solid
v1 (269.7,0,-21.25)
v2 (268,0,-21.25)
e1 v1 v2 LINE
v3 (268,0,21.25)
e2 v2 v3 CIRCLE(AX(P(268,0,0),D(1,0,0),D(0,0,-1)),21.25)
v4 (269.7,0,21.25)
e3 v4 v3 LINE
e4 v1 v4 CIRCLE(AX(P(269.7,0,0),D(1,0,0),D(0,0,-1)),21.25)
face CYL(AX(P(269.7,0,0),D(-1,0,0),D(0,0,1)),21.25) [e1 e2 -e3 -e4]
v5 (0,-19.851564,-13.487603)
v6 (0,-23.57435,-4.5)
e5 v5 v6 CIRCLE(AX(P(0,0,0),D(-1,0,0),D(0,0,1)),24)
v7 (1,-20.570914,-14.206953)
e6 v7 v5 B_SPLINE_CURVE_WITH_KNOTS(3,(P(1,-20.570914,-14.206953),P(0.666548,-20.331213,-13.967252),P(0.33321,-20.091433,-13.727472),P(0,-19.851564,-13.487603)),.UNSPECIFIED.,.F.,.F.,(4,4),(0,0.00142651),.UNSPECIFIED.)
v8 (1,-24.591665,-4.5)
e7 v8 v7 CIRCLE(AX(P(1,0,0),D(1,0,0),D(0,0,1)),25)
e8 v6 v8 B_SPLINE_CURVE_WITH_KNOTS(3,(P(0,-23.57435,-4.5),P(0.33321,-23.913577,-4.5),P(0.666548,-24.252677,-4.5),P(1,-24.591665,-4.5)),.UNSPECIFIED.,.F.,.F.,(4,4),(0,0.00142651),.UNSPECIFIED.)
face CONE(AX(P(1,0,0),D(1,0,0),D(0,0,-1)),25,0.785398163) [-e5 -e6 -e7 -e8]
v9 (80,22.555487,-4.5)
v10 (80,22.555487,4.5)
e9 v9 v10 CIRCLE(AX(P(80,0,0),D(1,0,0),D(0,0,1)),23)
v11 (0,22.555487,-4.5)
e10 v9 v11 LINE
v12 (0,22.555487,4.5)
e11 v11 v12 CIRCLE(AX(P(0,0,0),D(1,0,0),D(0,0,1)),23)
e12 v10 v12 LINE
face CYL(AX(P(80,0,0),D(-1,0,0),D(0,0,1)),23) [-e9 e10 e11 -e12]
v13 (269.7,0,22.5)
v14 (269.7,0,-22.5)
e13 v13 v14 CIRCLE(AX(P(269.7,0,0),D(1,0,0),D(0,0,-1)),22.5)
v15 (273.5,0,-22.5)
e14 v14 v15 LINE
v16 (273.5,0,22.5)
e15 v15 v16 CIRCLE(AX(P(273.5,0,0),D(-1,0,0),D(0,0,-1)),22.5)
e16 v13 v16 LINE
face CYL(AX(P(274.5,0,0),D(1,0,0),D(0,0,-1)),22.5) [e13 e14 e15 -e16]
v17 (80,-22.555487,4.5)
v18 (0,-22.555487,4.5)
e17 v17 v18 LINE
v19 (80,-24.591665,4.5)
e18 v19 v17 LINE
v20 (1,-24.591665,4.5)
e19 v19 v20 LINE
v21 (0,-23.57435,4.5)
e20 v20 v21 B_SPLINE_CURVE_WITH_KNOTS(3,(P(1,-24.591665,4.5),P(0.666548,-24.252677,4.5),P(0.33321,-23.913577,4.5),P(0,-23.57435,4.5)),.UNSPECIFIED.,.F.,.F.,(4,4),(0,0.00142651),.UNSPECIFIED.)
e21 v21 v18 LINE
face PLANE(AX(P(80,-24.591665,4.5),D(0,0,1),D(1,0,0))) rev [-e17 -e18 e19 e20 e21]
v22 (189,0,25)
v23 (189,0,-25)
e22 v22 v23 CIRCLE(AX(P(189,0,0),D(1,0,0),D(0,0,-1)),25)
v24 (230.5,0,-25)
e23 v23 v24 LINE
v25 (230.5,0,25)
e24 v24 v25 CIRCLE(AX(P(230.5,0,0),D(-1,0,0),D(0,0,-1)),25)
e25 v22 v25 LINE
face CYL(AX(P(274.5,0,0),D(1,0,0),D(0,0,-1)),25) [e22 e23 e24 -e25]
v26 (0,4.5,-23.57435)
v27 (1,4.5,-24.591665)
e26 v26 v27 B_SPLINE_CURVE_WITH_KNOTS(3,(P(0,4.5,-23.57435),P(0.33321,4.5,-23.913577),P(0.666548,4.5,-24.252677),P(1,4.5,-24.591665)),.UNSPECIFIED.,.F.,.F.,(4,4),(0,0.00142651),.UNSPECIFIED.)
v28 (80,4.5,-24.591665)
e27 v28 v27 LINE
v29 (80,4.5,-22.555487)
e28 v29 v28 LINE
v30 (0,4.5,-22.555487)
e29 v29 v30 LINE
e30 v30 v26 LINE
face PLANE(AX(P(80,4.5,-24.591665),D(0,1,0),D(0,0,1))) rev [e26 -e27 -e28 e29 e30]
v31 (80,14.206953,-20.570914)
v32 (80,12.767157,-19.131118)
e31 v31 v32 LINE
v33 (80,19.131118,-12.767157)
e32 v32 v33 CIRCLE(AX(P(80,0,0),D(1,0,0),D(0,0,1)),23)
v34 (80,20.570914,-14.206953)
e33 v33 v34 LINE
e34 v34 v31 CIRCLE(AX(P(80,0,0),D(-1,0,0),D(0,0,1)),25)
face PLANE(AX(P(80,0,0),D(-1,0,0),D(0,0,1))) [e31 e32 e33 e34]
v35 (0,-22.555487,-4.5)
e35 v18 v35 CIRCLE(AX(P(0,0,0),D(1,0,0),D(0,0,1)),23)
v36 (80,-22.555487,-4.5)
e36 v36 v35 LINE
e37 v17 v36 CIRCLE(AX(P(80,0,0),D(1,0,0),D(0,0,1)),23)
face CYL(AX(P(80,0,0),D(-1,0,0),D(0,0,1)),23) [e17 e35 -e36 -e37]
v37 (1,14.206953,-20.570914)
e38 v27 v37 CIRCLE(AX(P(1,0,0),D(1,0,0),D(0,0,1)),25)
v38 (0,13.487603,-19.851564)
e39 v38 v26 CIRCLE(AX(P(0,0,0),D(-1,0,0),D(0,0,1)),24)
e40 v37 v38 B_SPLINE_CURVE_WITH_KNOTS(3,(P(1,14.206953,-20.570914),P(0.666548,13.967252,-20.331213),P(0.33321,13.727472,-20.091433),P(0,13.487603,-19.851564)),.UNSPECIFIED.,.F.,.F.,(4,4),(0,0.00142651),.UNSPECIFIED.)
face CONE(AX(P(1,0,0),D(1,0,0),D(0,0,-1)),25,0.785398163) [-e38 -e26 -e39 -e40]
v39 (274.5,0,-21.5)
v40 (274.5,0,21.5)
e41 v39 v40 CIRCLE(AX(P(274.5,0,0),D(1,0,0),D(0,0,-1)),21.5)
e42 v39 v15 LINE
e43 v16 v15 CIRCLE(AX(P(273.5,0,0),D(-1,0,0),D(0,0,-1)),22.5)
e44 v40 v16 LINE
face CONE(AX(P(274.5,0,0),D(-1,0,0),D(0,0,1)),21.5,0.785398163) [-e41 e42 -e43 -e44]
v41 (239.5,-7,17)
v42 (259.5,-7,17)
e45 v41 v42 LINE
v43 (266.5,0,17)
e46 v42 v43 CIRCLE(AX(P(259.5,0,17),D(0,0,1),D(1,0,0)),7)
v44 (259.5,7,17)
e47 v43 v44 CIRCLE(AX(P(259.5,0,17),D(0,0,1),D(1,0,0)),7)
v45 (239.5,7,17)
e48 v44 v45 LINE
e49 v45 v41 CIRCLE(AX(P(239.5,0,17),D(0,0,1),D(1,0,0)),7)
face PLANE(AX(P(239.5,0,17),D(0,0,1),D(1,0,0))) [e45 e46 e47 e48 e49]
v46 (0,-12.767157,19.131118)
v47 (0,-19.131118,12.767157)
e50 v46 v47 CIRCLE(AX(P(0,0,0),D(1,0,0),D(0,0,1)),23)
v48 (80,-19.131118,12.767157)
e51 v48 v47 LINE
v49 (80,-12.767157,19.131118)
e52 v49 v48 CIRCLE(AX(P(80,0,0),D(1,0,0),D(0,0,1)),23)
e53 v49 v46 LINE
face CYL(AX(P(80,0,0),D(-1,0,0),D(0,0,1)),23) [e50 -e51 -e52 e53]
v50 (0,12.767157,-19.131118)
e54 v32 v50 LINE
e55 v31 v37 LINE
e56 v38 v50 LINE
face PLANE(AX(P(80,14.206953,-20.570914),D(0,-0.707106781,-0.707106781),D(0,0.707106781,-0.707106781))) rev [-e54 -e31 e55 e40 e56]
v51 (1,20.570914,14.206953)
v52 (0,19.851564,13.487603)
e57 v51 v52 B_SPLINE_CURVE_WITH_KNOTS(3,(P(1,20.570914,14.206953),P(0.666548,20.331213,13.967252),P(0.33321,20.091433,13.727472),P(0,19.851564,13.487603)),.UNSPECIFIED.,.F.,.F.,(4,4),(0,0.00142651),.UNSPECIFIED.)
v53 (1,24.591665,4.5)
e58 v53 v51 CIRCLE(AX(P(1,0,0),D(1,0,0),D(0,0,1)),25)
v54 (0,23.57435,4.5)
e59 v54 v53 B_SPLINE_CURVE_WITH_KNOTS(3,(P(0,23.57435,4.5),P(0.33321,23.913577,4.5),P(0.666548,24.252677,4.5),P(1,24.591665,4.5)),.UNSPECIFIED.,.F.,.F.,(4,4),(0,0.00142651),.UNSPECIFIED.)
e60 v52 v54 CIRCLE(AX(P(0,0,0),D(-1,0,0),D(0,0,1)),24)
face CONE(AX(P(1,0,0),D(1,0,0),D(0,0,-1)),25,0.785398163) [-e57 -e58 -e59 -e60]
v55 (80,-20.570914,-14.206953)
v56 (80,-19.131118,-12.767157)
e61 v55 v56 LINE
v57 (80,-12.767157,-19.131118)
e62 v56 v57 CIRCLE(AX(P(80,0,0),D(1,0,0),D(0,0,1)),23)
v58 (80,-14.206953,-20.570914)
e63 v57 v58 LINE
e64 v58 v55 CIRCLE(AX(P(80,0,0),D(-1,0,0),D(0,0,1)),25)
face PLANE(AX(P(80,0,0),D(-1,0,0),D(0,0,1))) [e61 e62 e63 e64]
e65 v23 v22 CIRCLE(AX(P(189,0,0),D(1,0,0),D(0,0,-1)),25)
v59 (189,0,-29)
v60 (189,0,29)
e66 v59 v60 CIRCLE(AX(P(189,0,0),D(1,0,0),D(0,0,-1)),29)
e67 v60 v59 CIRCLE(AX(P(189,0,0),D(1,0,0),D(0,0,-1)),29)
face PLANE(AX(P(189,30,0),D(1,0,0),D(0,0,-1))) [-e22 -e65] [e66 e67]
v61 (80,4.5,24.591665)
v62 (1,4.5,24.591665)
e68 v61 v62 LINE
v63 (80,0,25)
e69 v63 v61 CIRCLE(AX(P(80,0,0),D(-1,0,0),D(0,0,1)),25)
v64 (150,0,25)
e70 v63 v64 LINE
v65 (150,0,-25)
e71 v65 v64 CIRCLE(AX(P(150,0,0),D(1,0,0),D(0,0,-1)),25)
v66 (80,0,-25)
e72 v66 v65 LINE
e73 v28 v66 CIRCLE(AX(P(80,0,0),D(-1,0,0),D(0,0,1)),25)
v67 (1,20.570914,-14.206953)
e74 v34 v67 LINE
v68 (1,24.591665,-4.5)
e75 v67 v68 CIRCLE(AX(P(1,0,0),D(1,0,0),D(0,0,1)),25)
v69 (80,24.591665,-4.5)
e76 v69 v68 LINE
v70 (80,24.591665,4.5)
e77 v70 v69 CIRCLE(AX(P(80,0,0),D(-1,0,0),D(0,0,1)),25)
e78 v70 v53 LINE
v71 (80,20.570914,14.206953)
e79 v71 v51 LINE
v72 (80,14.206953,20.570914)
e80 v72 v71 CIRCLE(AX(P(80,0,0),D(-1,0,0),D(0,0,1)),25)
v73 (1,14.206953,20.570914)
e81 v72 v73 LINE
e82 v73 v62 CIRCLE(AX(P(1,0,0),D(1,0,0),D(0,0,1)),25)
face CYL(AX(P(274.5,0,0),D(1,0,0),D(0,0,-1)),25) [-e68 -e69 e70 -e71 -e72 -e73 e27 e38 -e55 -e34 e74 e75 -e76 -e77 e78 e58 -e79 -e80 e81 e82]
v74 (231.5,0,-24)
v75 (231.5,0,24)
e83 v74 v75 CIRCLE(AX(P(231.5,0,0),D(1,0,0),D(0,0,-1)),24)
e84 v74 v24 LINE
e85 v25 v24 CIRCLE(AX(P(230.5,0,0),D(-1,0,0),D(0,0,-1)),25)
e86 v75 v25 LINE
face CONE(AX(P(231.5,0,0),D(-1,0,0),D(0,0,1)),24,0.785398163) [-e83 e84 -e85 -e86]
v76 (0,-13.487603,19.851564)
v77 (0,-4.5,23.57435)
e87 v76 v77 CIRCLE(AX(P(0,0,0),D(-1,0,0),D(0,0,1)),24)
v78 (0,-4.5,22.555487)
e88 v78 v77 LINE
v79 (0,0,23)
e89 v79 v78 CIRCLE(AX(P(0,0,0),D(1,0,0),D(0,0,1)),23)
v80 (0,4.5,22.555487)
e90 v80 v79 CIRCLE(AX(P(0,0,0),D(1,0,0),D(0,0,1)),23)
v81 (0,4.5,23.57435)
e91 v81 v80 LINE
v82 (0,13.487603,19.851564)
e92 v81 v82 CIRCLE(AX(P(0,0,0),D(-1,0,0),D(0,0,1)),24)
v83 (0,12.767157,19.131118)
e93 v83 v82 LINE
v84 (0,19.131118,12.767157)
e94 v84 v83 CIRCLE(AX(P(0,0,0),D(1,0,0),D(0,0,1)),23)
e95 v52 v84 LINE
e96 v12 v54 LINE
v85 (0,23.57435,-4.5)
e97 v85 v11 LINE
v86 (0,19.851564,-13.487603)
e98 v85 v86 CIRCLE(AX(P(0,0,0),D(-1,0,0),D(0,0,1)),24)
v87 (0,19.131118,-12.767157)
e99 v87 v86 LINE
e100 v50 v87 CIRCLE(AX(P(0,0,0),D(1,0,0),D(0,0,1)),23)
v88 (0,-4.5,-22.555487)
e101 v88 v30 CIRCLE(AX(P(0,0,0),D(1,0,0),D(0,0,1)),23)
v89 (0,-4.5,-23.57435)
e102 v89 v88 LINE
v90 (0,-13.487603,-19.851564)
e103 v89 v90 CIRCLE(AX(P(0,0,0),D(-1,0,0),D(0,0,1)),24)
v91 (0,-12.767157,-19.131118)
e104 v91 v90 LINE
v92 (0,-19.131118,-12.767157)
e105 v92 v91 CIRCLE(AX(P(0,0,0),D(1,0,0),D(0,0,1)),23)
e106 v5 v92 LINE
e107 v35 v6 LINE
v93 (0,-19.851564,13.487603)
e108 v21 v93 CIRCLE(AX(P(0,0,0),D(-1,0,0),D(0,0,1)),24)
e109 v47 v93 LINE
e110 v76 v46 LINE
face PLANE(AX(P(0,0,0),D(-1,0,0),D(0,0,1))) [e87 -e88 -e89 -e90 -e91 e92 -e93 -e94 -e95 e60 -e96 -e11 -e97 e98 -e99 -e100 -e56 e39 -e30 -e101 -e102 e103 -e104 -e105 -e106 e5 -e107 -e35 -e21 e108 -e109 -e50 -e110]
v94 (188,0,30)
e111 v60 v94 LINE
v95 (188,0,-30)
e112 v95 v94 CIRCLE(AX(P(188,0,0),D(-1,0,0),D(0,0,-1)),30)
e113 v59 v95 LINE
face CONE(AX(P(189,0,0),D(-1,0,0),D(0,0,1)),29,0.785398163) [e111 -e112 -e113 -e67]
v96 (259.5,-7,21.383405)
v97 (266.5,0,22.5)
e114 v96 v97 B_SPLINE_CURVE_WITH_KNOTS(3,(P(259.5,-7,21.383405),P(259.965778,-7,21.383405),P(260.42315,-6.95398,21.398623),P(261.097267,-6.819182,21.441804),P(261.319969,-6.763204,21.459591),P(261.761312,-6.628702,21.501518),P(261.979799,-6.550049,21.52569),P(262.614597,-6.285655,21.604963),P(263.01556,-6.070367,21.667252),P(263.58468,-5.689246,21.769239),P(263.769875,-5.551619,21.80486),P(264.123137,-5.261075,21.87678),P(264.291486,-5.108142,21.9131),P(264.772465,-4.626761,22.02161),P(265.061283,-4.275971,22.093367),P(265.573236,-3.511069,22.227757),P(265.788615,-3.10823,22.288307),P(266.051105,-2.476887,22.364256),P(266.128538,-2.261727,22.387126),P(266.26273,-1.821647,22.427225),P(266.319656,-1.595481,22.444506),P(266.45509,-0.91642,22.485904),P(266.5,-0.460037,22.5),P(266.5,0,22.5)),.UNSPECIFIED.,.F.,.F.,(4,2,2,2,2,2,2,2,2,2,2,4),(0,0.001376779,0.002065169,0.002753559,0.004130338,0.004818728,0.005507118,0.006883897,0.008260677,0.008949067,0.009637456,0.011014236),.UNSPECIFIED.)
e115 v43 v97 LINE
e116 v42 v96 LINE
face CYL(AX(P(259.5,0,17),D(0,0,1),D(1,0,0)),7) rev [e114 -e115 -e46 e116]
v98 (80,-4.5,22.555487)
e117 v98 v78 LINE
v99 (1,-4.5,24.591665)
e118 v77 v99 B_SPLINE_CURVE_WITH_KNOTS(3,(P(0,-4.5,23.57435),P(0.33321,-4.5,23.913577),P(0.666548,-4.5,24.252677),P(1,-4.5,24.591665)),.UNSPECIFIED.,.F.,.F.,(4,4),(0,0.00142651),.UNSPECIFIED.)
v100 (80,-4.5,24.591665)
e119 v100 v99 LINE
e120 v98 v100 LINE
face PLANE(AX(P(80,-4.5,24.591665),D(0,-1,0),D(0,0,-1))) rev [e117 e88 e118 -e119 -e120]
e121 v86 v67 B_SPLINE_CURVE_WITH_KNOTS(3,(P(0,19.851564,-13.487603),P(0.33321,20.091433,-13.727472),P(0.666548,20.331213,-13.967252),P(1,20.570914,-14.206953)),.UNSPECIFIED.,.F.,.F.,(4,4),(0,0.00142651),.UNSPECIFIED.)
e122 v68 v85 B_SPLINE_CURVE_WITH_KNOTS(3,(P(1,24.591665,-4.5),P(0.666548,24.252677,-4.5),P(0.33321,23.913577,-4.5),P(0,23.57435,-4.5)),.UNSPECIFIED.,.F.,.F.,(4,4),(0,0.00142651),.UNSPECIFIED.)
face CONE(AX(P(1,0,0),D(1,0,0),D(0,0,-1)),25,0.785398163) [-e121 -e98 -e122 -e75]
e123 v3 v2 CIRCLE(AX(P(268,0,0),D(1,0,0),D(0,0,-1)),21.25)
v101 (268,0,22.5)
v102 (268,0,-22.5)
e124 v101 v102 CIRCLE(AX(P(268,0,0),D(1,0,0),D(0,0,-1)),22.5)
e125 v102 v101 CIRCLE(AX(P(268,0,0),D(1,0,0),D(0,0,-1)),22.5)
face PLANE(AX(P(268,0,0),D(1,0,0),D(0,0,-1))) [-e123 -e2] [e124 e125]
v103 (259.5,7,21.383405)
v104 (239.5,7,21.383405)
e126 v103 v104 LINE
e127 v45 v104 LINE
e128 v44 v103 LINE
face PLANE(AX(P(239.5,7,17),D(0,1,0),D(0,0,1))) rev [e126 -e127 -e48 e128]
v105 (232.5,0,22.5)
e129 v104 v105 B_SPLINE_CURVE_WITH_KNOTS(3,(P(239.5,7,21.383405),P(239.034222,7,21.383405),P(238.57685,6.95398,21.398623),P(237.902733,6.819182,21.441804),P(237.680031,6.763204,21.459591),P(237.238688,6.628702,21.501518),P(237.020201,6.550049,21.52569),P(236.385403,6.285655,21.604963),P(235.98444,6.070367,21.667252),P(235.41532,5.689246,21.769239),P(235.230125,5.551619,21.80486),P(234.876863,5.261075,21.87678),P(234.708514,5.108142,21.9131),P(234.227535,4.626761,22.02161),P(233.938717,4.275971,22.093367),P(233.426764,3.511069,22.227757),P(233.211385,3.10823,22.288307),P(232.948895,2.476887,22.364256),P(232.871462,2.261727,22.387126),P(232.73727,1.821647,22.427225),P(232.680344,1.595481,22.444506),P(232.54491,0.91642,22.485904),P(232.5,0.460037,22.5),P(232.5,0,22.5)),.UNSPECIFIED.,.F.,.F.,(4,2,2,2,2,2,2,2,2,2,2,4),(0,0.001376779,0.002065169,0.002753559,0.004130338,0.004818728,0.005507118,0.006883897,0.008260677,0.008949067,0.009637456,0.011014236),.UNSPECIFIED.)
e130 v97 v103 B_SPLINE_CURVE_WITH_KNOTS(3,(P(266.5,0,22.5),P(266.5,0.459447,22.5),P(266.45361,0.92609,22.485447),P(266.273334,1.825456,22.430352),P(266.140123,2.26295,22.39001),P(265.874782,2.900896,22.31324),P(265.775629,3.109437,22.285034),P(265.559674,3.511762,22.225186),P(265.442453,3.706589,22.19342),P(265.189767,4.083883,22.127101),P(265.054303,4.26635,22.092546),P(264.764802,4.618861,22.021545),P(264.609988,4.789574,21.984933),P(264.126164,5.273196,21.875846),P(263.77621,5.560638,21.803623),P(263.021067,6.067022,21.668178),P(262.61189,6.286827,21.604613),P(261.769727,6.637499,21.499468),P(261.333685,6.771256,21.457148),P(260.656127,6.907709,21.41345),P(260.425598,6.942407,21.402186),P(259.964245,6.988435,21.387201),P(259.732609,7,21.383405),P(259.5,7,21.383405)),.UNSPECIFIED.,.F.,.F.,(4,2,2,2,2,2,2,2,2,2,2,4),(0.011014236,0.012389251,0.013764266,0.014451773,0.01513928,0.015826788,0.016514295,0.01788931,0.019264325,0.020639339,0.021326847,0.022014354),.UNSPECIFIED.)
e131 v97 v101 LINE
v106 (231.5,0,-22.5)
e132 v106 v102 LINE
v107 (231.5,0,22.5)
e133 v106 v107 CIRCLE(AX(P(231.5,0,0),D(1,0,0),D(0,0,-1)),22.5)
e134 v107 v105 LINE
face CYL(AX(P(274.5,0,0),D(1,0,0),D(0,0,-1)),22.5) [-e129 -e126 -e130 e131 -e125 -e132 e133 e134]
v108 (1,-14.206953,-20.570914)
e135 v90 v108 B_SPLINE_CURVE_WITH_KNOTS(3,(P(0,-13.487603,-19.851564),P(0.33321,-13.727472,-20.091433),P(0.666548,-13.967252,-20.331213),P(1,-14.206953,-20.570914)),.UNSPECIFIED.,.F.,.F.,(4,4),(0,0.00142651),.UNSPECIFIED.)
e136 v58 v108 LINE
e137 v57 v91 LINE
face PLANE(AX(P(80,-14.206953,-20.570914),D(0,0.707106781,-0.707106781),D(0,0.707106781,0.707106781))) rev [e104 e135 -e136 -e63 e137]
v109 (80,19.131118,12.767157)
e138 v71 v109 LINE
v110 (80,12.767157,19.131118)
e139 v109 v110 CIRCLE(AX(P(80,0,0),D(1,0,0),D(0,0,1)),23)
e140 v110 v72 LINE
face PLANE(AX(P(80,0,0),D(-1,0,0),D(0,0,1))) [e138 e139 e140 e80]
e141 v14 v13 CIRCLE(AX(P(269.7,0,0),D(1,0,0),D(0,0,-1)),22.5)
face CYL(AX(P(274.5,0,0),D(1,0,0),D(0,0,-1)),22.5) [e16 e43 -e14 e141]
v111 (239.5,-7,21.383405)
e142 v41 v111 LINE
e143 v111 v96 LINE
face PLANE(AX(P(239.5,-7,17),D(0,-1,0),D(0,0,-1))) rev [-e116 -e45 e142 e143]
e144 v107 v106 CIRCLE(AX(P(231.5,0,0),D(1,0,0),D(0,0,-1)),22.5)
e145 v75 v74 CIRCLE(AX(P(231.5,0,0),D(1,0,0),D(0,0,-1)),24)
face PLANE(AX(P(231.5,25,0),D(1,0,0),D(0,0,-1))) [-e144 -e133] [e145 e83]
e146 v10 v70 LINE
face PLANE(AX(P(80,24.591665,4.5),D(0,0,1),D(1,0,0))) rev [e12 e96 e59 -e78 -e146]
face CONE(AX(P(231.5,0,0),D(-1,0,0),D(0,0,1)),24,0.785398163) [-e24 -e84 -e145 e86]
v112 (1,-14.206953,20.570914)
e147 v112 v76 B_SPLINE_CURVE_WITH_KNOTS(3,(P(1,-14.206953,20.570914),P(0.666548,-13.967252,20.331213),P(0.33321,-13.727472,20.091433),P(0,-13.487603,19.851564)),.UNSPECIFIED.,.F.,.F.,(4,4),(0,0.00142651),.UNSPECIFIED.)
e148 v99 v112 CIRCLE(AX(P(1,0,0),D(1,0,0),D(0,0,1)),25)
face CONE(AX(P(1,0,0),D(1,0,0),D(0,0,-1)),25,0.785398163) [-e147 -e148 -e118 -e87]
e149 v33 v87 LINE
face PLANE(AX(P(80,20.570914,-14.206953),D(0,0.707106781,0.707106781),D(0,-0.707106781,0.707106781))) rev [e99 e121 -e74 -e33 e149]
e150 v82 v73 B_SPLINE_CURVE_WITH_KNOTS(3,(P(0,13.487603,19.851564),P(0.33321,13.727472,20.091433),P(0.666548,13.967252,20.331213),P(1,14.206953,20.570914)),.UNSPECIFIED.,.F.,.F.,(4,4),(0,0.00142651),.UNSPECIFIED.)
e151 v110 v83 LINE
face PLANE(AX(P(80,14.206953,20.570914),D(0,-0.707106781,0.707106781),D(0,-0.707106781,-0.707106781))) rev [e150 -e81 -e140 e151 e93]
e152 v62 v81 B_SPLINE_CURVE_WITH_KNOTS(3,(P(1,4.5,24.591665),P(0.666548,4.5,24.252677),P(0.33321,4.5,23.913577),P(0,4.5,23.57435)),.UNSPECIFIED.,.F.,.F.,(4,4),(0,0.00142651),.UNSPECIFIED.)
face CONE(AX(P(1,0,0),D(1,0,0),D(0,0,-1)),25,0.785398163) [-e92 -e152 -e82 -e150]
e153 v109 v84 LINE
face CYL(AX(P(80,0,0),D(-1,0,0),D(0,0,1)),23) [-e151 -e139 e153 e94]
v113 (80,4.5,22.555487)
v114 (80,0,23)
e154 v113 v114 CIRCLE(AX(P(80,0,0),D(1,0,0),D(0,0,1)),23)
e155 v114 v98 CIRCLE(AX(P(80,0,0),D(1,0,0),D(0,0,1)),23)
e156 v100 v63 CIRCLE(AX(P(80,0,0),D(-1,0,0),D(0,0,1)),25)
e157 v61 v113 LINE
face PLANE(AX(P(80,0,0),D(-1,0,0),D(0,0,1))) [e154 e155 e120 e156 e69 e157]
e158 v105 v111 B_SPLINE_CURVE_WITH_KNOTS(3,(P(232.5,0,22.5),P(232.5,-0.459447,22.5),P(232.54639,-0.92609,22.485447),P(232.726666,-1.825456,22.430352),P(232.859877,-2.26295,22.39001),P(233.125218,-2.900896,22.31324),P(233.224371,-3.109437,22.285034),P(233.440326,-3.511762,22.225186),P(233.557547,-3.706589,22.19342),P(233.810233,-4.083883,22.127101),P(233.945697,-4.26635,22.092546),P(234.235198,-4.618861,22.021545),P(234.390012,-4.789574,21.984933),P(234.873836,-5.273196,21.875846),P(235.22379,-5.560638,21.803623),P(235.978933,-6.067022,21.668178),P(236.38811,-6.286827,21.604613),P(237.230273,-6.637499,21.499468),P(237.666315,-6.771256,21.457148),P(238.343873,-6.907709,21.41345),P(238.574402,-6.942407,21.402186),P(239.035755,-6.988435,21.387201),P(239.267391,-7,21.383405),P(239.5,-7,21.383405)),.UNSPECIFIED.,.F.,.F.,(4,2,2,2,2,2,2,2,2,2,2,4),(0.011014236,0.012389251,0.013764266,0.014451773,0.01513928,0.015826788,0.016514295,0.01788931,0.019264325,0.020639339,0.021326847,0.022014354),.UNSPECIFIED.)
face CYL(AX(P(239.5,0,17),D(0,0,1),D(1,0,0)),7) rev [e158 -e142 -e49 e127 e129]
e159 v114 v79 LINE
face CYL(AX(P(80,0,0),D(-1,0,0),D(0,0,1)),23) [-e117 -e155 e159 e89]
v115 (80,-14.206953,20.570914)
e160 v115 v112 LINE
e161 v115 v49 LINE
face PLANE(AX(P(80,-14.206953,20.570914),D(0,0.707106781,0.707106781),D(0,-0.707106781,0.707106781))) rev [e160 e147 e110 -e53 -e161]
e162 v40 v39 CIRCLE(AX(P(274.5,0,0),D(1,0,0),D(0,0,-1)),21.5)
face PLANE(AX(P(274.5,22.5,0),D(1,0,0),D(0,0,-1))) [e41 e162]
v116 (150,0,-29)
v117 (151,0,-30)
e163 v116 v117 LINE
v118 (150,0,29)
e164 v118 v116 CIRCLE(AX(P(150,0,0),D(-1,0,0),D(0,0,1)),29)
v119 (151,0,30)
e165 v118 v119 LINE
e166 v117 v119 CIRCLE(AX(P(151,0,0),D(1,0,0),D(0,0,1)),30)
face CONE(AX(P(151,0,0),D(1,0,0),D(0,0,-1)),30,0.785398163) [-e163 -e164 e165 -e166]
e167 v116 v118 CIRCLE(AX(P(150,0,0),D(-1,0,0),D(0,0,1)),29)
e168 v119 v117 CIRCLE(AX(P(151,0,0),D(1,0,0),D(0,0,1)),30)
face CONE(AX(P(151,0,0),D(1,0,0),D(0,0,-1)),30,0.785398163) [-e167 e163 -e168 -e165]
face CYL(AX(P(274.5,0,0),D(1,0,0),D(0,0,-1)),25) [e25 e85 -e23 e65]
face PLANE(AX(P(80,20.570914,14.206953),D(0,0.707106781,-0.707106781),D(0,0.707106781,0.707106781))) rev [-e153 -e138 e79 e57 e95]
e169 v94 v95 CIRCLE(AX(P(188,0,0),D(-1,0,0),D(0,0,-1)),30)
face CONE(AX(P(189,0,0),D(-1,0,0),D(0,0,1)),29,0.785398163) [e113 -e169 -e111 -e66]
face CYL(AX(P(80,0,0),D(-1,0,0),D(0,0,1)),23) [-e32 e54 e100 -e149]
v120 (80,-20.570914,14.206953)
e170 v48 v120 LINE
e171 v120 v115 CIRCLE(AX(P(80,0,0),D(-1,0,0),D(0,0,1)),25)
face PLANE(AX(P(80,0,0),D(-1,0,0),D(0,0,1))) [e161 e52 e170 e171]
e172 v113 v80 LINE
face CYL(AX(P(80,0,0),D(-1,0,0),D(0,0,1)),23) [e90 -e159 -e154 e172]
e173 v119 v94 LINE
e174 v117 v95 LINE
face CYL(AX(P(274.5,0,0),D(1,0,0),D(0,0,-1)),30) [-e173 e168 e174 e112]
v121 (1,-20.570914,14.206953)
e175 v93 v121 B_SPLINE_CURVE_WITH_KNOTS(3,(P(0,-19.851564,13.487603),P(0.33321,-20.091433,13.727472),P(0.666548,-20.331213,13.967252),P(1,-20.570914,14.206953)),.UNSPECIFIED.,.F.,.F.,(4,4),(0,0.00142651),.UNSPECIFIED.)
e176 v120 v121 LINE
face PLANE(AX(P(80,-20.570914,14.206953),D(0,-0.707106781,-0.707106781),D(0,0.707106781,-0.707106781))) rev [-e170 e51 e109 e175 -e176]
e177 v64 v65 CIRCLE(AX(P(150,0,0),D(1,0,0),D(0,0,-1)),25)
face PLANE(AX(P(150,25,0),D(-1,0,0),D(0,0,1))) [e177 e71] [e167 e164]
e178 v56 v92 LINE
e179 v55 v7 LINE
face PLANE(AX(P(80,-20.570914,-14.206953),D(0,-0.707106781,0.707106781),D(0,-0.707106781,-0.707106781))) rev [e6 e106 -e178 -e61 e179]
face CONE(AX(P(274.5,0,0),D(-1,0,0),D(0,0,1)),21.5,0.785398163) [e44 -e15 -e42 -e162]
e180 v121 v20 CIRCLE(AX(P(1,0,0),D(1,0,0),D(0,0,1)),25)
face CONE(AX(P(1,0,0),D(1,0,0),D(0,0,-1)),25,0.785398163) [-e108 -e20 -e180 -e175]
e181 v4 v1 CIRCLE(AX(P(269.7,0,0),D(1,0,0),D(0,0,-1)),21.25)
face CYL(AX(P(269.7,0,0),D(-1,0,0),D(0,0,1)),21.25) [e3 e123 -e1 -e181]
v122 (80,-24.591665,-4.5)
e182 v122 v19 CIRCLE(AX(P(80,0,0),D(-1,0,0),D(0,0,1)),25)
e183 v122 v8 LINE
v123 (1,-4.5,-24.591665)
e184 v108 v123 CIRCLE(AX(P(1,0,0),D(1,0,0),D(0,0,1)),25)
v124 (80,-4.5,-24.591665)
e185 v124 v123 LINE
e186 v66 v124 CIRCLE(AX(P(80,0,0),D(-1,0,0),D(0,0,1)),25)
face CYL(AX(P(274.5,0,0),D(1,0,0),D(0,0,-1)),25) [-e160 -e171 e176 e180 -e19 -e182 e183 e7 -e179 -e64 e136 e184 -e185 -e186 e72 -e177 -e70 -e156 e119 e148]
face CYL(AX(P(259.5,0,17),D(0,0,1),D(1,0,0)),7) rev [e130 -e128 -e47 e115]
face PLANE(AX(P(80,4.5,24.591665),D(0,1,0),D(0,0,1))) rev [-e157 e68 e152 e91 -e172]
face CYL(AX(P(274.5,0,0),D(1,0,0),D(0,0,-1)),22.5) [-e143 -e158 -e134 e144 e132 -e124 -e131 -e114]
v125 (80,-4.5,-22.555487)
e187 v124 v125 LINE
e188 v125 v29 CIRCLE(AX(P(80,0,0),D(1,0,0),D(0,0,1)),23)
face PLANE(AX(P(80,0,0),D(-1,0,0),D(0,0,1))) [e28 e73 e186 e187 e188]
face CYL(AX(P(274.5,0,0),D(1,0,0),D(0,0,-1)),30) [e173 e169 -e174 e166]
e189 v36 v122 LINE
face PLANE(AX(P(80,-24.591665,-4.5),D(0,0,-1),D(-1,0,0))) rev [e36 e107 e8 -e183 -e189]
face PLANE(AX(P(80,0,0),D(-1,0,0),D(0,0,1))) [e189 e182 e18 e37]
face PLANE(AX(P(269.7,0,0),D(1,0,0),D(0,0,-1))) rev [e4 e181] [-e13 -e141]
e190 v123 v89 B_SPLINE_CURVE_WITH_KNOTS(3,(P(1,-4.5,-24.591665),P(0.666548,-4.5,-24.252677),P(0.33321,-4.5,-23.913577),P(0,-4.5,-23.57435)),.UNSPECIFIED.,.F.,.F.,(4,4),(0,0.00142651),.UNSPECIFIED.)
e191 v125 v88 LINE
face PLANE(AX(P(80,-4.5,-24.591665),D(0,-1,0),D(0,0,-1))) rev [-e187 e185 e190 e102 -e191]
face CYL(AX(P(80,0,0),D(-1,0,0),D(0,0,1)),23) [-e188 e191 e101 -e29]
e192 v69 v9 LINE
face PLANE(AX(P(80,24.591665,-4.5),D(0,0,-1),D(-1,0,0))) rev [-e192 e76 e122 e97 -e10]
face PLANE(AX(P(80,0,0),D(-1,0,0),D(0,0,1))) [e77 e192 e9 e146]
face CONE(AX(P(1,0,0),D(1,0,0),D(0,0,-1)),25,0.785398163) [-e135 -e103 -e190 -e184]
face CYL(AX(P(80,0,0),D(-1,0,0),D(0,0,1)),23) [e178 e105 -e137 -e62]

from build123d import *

# Parameters (mm, degrees)
CHAMFER_1_SIZE      = 1
CUT_EXTRUDE_START   = 1.7
SKETCH_2_R          = 22.5
SKETCH_2_R_2        = 21.25
CUT_EXTRUDE_1_DEPTH = 1.7
CUT_EXTRUDE_2_DEPTH = 5.5
CUT_EXTRUDE_START_2 = -80
CUT_EXTRUDE_3_DEPTH = 80
CHAMFER_2_SIZE      = 1


with BuildPart() as part:
    # 草图1 → 旋转1 (revolve)
    with BuildSketch(Plane.XY, mode=Mode.PRIVATE) as revolve_1_sk:
        Polygon((0, 0), (0, 25), (150, 25), (150, 30), (189, 30), (189, 25), (231.5, 25), (231.5, 22.5), (274.5, 22.5), (274.5, 0), align=None)
    revolve(revolve_1_sk.sketch.rotate(Axis((274.5, 0, 0), (-1, 0, 0)), 90), axis=Axis((274.5, 0, 0), (-1, 0, 0)))

    # 倒角1
    chamfer_1_edges = [part.edges().sort_by_distance(p)[0] for p in [
        (274.5, 0, 22.5),
        (231.5, 0, 25),
        (189, 0, 30),
        (150, 0, 30),
    ]]
    chamfer(chamfer_1_edges, length=CHAMFER_1_SIZE)

    # 草图2 → 切除-拉伸1 (cut)
    with BuildSketch(Plane(origin=(268, 0, 0), x_dir=(0, 0, -1), z_dir=(1, 0, 0)).offset(CUT_EXTRUDE_START)):
        Circle(SKETCH_2_R)
        Circle(SKETCH_2_R_2, mode=Mode.SUBTRACT)
    extrude(amount=-CUT_EXTRUDE_1_DEPTH, mode=Mode.SUBTRACT)

    # 草图3 → 切除-拉伸2 (cut)
    with BuildSketch(Plane.XY.offset(22.5)):
        with BuildLine():
            Line((239.5, 7), (259.5, 7))
            ThreePointArc((259.5, 7), (266.5, 0), (259.5, -7))
            Line((259.5, -7), (239.5, -7))
            ThreePointArc((239.5, -7), (232.5, 0), (239.5, 7))
        make_face()
    extrude(amount=-CUT_EXTRUDE_2_DEPTH, mode=Mode.SUBTRACT)

    # 草图4 → 切除-拉伸3 (cut)
    with BuildSketch(Plane.ZY.offset(CUT_EXTRUDE_START_2)):
        with BuildLine():
            Line((-4.5, 24.591665255), (-4.5, 22.555487137))
            ThreePointArc((-4.5, 22.555487137), (0, 23), (4.5, 22.555487137))
            Line((4.5, 22.555487137), (4.5, 24.591665255))
            ThreePointArc((4.5, 24.591665255), (0, 25), (-4.5, 24.591665255))
        make_face()
        with BuildLine():
            Line((20.570913778, 14.206952747), (19.131118423, 12.767157392))
            ThreePointArc((19.131118423, 12.767157392), (16.263455967, 16.263455967), (12.767157392, 19.131118423))
            Line((12.767157392, 19.131118423), (14.206952747, 20.570913778))
            ThreePointArc((14.206952747, 20.570913778), (17.67766953, 17.67766953), (20.570913778, 14.206952747))
        make_face()
        with BuildLine():
            Line((24.591665255, -4.5), (22.555487137, -4.5))
            ThreePointArc((22.555487137, -4.5), (23, 0), (22.555487137, 4.5))
            Line((22.555487137, 4.5), (24.591665255, 4.5))
            ThreePointArc((24.591665255, 4.5), (25, 0), (24.591665255, -4.5))
        make_face()
        with BuildLine():
            Line((14.206952747, -20.570913778), (12.767157392, -19.131118423))
            ThreePointArc((12.767157392, -19.131118423), (16.263455967, -16.263455967), (19.131118423, -12.767157392))
            Line((19.131118423, -12.767157392), (20.570913778, -14.206952747))
            ThreePointArc((20.570913778, -14.206952747), (17.67766953, -17.67766953), (14.206952747, -20.570913778))
        make_face()
        with BuildLine():
            Line((-4.5, -24.591665255), (-4.5, -22.555487137))
            ThreePointArc((-4.5, -22.555487137), (0, -23), (4.5, -22.555487137))
            Line((4.5, -22.555487137), (4.5, -24.591665255))
            ThreePointArc((4.5, -24.591665255), (0, -25), (-4.5, -24.591665255))
        make_face()
        with BuildLine():
            Line((-20.570913778, -14.206952747), (-19.131118423, -12.767157392))
            ThreePointArc((-19.131118423, -12.767157392), (-16.263455967, -16.263455967), (-12.767157392, -19.131118423))
            Line((-12.767157392, -19.131118423), (-14.206952747, -20.570913778))
            ThreePointArc((-14.206952747, -20.570913778), (-17.67766953, -17.67766953), (-20.570913778, -14.206952747))
        make_face()
        with BuildLine():
            Line((-24.591665255, 4.5), (-22.555487137, 4.5))
            ThreePointArc((-22.555487137, 4.5), (-23, 0), (-22.555487137, -4.5))
            Line((-22.555487137, -4.5), (-24.591665255, -4.5))
            ThreePointArc((-24.591665255, -4.5), (-25, 0), (-24.591665255, 4.5))
        make_face()
        with BuildLine():
            Line((-14.206952747, 20.570913778), (-12.767157392, 19.131118423))
            ThreePointArc((-12.767157392, 19.131118423), (-16.263455967, 16.263455967), (-19.131118423, 12.767157392))
            Line((-19.131118423, 12.767157392), (-20.570913778, 14.206952747))
            ThreePointArc((-20.570913778, 14.206952747), (-17.67766953, 17.67766953), (-14.206952747, 20.570913778))
        make_face()
    extrude(amount=CUT_EXTRUDE_3_DEPTH, mode=Mode.SUBTRACT)

    # 倒角2
    chamfer_2_edges = [part.edges().sort_by_distance(p)[0] for p in [
        (0, 23.096988313, 9.567085809),
        (0, 9.567085809, 23.096988313),
        (0, -9.567085809, 23.096988313),
        (0, -23.096988313, 9.567085809),
        (0, -23.096988313, -9.567085809),
        (0, -9.567085809, -23.096988313),
        (0, 9.567085809, -23.096988313),
        (0, 23.096988313, -9.567085809),
    ]]
    chamfer(chamfer_2_edges, length=CHAMFER_2_SIZE)


solid = part.part
